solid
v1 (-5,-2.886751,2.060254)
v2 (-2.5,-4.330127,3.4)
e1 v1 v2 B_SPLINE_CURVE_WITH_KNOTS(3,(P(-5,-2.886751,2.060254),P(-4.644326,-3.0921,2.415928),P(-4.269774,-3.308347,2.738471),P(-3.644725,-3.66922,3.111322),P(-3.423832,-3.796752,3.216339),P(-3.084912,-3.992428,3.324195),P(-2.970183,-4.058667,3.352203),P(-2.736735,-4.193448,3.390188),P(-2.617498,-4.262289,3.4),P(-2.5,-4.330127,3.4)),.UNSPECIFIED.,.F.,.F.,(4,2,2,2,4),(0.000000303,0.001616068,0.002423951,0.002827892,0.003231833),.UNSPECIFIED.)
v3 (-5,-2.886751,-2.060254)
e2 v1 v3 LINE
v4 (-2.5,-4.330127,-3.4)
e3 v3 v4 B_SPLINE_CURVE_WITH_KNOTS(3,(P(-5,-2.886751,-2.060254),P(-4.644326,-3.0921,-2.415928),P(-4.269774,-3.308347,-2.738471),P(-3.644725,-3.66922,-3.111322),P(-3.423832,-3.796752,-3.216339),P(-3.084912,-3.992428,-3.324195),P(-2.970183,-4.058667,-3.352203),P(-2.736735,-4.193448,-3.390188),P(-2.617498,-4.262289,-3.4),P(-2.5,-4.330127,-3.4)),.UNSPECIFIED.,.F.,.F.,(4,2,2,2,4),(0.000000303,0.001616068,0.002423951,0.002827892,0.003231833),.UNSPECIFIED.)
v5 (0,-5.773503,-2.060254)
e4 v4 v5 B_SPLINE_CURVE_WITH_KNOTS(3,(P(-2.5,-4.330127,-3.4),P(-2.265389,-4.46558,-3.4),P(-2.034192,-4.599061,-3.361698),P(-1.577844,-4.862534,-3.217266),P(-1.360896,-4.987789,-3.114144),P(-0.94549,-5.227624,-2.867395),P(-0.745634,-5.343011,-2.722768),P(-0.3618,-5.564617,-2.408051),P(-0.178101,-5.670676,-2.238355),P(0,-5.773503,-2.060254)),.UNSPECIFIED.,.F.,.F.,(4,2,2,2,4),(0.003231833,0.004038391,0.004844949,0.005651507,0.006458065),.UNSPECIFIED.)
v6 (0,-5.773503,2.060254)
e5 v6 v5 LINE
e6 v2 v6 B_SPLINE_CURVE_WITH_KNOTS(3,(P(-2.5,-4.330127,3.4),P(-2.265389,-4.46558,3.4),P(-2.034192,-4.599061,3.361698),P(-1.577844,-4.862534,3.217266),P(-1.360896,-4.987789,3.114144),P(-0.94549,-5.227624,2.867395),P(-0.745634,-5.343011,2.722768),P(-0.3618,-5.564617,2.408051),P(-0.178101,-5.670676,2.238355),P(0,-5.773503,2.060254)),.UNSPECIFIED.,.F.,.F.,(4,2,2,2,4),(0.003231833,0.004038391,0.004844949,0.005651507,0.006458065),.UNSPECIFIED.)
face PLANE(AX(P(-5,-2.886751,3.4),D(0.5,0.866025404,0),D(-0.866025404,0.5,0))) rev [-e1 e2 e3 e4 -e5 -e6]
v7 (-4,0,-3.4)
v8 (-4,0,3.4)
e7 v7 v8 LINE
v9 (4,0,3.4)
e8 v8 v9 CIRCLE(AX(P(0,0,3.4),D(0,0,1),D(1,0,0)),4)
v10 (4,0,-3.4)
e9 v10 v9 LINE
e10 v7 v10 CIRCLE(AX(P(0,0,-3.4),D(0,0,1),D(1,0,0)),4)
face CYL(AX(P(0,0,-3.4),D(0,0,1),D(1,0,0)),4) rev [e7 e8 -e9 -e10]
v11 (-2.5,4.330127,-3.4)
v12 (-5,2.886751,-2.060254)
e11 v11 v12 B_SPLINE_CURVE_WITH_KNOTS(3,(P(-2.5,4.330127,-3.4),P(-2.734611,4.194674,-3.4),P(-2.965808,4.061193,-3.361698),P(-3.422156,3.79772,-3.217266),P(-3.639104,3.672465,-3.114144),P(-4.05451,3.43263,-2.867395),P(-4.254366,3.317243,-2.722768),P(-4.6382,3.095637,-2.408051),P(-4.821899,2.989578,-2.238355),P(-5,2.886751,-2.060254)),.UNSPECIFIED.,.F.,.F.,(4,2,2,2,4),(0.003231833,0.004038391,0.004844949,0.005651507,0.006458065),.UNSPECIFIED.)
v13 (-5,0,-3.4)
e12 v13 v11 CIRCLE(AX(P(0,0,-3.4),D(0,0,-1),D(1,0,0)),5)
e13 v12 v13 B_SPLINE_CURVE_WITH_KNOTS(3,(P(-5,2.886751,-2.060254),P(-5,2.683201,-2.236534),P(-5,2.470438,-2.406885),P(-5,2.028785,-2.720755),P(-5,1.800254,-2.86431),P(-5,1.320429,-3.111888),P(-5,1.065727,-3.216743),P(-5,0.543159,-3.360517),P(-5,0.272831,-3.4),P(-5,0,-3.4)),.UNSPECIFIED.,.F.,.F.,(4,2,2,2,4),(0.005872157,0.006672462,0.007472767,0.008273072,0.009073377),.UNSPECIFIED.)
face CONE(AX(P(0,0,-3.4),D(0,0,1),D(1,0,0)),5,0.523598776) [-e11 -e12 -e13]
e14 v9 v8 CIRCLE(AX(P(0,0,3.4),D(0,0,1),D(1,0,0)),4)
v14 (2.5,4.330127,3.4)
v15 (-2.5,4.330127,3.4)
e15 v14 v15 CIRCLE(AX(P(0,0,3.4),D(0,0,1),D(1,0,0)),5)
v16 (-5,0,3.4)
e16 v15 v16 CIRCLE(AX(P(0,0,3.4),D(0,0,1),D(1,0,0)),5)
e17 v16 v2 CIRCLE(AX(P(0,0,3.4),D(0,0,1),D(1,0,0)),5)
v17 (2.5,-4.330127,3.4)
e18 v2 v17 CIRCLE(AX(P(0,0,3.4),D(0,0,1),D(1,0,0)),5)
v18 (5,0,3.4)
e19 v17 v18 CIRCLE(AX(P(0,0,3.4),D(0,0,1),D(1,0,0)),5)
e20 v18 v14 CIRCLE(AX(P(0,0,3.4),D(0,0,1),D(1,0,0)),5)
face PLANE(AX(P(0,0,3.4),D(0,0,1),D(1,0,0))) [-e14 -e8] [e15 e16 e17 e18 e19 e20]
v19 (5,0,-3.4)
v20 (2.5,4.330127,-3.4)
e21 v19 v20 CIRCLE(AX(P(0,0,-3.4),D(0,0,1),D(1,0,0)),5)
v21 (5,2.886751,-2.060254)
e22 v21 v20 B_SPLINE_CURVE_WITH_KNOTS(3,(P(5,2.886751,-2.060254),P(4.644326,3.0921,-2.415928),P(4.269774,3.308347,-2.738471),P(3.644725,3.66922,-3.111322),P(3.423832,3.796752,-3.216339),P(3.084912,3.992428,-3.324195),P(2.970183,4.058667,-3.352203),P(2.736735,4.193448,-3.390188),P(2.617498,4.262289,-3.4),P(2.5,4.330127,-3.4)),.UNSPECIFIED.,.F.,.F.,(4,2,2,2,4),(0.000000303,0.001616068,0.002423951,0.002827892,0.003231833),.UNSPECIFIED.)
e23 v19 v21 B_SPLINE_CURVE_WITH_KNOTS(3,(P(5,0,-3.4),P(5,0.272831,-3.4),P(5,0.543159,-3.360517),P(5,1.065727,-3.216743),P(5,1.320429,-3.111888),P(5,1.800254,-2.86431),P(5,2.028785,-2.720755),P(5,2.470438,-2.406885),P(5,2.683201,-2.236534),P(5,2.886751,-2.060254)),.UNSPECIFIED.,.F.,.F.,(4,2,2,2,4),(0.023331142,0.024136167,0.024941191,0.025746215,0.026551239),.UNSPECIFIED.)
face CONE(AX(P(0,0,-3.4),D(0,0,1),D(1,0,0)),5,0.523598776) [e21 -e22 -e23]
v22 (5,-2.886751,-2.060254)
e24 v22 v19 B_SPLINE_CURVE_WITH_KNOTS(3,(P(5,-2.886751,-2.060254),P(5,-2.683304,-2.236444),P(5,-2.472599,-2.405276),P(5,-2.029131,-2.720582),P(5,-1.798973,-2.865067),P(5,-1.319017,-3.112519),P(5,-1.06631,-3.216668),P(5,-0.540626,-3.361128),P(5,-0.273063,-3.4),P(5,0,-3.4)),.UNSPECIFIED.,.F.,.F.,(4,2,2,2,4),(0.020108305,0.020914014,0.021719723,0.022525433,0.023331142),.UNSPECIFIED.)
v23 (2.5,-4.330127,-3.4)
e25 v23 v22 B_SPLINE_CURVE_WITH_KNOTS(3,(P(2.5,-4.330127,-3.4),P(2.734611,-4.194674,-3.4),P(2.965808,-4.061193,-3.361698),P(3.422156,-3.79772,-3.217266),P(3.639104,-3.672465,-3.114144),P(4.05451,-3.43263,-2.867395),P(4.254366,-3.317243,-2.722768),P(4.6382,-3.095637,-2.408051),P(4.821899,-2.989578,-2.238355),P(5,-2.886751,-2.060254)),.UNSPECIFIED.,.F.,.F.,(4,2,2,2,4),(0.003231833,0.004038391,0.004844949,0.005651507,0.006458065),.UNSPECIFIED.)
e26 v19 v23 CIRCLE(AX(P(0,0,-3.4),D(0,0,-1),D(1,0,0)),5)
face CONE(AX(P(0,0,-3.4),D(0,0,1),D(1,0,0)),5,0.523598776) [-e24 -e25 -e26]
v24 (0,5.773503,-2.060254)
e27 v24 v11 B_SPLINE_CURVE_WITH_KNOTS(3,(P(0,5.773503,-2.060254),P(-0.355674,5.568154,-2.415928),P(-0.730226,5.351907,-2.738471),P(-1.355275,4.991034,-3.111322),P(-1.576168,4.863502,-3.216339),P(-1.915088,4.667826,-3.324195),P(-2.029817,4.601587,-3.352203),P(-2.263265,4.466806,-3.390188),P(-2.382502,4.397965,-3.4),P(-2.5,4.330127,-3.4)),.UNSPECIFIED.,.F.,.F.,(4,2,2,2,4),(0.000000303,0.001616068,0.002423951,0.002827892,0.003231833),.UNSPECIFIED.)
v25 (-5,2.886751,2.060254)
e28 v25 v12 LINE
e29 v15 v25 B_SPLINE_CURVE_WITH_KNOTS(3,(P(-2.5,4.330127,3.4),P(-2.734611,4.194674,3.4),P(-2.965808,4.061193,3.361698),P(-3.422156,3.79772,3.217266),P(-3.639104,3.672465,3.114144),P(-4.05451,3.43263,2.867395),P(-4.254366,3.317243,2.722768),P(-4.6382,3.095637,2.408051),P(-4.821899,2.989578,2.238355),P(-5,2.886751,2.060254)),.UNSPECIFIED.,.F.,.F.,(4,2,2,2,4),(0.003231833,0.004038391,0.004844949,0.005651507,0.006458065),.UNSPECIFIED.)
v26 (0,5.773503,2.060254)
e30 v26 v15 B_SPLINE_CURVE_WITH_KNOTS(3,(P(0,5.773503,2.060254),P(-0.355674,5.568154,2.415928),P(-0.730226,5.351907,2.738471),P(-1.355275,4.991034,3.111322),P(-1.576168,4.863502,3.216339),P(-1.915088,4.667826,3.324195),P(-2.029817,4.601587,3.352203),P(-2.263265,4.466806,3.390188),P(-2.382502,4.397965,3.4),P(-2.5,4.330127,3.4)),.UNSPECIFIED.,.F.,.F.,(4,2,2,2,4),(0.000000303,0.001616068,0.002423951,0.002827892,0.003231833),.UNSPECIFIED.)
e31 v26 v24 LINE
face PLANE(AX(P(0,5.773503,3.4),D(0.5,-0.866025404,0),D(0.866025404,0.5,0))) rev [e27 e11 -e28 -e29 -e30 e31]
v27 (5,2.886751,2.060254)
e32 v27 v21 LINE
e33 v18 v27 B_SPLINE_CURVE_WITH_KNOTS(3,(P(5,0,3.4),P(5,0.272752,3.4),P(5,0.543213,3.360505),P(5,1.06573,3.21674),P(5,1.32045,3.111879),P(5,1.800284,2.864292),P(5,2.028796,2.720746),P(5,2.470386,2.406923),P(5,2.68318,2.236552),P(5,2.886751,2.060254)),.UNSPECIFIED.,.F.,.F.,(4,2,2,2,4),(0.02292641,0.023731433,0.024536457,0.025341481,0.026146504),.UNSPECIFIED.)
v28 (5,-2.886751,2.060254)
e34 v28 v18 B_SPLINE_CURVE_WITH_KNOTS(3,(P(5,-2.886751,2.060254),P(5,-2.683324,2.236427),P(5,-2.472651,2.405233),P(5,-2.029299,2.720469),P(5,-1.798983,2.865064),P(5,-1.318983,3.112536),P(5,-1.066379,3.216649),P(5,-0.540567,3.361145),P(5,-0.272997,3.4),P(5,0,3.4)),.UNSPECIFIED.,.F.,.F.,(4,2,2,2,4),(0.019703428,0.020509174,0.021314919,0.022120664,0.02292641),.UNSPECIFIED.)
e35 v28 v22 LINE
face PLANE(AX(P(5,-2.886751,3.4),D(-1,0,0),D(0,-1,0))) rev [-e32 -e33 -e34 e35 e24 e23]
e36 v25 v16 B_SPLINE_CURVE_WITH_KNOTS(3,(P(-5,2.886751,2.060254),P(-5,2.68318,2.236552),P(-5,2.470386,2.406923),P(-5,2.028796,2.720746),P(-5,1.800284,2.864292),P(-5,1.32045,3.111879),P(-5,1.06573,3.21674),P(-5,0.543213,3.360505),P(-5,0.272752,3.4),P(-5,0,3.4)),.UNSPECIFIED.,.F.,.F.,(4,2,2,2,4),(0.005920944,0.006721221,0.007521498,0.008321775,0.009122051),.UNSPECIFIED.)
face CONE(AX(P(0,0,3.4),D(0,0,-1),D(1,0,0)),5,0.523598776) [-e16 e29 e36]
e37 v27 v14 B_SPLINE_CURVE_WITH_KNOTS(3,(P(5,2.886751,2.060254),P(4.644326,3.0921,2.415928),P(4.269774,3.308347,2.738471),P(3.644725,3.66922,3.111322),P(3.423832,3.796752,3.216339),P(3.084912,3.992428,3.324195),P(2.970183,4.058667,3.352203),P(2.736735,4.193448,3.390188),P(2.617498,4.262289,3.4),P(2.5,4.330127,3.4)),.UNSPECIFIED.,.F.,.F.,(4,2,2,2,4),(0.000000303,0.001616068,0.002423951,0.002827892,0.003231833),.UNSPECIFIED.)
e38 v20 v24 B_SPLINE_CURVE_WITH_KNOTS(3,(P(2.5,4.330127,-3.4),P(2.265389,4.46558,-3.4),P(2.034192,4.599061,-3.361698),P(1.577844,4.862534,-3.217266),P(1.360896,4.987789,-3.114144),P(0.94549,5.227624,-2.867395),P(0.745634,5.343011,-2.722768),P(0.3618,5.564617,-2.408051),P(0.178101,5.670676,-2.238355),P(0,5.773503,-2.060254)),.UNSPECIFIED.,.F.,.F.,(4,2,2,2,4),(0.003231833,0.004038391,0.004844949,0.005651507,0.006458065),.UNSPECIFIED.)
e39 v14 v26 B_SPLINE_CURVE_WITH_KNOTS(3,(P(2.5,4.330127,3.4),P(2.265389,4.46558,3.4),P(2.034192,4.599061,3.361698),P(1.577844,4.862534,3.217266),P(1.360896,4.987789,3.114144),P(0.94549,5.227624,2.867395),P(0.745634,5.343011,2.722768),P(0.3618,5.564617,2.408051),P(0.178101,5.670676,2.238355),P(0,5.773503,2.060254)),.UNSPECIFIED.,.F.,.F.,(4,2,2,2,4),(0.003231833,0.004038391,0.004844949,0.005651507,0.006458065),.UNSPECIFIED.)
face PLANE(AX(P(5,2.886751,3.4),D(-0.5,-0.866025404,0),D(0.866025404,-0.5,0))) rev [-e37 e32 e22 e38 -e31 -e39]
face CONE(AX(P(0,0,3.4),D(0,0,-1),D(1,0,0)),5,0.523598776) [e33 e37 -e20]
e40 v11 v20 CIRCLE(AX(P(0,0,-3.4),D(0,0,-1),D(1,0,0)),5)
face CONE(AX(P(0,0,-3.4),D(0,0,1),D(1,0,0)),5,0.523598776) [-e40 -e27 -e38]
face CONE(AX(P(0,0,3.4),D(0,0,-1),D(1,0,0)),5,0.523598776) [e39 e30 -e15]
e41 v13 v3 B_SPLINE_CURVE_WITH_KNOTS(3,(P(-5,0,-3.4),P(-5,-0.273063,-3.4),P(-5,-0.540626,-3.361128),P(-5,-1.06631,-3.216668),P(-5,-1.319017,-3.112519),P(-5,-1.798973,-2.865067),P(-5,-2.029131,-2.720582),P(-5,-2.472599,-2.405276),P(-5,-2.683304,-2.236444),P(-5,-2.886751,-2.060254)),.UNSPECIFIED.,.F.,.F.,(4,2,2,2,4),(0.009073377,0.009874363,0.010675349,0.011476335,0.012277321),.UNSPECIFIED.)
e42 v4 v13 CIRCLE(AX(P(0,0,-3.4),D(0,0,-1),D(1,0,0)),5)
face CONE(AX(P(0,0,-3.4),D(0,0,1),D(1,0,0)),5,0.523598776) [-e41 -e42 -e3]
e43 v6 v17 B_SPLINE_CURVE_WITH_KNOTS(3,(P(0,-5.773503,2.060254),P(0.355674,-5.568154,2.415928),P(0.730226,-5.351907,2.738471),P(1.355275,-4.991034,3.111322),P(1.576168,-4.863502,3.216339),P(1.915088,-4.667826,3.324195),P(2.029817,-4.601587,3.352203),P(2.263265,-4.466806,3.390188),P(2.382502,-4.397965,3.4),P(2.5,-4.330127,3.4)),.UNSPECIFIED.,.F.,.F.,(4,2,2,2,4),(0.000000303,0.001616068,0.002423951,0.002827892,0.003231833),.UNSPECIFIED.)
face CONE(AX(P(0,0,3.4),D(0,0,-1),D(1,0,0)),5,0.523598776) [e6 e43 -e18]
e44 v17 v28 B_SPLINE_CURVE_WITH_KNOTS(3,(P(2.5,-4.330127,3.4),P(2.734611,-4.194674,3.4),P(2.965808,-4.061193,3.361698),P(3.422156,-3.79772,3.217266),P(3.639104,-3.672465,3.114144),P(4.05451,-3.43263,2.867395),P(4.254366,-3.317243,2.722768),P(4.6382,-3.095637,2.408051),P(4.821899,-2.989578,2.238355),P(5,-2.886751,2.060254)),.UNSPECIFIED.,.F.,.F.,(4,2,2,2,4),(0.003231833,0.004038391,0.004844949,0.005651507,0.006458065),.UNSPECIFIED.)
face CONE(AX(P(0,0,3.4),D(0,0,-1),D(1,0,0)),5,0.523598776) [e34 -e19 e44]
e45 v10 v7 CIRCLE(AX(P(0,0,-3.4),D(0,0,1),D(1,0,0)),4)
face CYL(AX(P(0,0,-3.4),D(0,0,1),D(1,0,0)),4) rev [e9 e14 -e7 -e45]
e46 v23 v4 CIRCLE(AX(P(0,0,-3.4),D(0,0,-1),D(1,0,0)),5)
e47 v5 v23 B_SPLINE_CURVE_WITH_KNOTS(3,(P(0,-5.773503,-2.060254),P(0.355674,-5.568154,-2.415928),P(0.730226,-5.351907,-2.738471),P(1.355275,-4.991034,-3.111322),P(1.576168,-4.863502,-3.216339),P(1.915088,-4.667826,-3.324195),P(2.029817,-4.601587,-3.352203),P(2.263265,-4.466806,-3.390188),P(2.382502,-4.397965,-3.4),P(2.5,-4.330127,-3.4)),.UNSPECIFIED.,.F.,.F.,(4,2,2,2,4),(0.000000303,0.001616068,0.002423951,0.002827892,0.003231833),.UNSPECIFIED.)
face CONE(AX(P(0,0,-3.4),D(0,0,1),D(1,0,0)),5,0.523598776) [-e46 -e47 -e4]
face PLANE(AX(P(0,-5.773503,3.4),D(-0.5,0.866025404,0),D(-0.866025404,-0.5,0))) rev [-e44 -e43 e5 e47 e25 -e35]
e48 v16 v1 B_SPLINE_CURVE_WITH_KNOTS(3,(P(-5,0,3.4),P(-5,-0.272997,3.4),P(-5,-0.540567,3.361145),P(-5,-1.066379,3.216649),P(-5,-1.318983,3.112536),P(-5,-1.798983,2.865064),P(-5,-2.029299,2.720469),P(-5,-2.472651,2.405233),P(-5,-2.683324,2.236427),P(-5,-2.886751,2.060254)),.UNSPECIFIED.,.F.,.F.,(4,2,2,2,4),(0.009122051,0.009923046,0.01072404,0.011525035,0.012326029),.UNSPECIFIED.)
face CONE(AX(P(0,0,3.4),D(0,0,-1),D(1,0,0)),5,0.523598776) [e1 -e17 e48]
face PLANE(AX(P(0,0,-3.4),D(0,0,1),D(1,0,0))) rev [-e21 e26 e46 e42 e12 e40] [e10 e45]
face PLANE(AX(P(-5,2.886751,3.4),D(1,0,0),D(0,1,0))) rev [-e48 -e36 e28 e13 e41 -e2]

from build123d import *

# Parameters (mm, degrees)
BOSS_EXTRUDE1_DEPTH     = 3.4
SKETCH2_OUTSIDE_W       = 23.196
SKETCH2_OUTSIDE_H       = 24.744
SKETCH2_OUTSIDE_R       = 5
CUT_EXTRUDE1_DEPTH      = 6.8
CUT_EXTRUDE1_DRAFT      = -30
MIRROR1_COPY_1_SKETCH_W = 23.196
MIRROR1_COPY_1_SKETCH_H = 24.744
MIRROR1_COPY_1_SKETCH_R = 5
MIRROR1_COPY_1_DEPTH    = 6.8
MIRROR1_COPY_1_DRAFT    = -30
SKETCH3_R               = 4
CUT_EXTRUDE3_DEPTH      = 6.8


with BuildPart() as part:
    # Sketch1 → Boss-Extrude1 (new, symmetric)
    with BuildSketch(Plane.XY):
        Polygon((0, 5.773502692), (-5, 2.886751346), (-5, -2.886751346), (0, -5.773502692), (5, -2.886751346), (5, 2.886751346), align=None)
    extrude(amount=BOSS_EXTRUDE1_DEPTH, both=True)


with BuildPart() as cut_extrude1_tool:
    # Sketch2 outside → Cut-Extrude1 (with draft: the straight prism first)
    with BuildSketch(Plane.XY.offset(3.4)):
        Rectangle(SKETCH2_OUTSIDE_W, SKETCH2_OUTSIDE_H)
        Circle(SKETCH2_OUTSIDE_R, mode=Mode.SUBTRACT)
    extrude(amount=-CUT_EXTRUDE1_DEPTH)
    # Cut-Extrude1: the draft: its side faces are tilted about the plane it starts from
    cut_extrude1_sides = [cut_extrude1_tool.faces().sort_by_distance(p)[0] for p in [
        (0, -12.372, 0),
        (11.598, 0, 0),
        (0, 12.372, 0),
        (-11.598, 0, 0),
        (-5, 0, 0),
    ]]
    draft(cut_extrude1_sides, Plane.XY.offset(3.4), CUT_EXTRUDE1_DRAFT)


with BuildPart() as part_1:
    add(part.part)

    # Cut-Extrude1: cut by cut_extrude1_tool
    add(cut_extrude1_tool.part, mode=Mode.SUBTRACT)


with BuildPart() as mirror1_copy_1_tool:
    # Mirror1 copy 1 sketch → Mirror1 copy 1 (with draft: the straight prism first)
    with BuildSketch(Plane(origin=(0, 0, -3.4), x_dir=(1, 0, 0), z_dir=(0, 0, -1))):
        Rectangle(MIRROR1_COPY_1_SKETCH_W, MIRROR1_COPY_1_SKETCH_H)
        Circle(MIRROR1_COPY_1_SKETCH_R, mode=Mode.SUBTRACT)
    extrude(amount=-MIRROR1_COPY_1_DEPTH)
    # Mirror1 copy 1: the draft: its side faces are tilted about the plane it starts from
    mirror1_copy_1_sides = [mirror1_copy_1_tool.faces().sort_by_distance(p)[0] for p in [
        (0, -12.372, 0),
        (11.598, 0, 0),
        (0, 12.372, 0),
        (-11.598, 0, 0),
        (-5, 0, 0),
    ]]
    draft(mirror1_copy_1_sides, Plane(origin=(0, 0, -3.4), x_dir=(1, 0, 0), z_dir=(0, 0, -1)), MIRROR1_COPY_1_DRAFT)


with BuildPart() as part_2:
    add(part_1.part)

    # Mirror1 copy 1: cut by mirror1_copy_1_tool
    add(mirror1_copy_1_tool.part, mode=Mode.SUBTRACT)

    # Sketch3 → Cut-Extrude3 (cut)
    with BuildSketch(Plane.XY.offset(3.4)):
        Circle(SKETCH3_R)
    extrude(amount=-CUT_EXTRUDE3_DEPTH, mode=Mode.SUBTRACT)


solid = part_2.part
